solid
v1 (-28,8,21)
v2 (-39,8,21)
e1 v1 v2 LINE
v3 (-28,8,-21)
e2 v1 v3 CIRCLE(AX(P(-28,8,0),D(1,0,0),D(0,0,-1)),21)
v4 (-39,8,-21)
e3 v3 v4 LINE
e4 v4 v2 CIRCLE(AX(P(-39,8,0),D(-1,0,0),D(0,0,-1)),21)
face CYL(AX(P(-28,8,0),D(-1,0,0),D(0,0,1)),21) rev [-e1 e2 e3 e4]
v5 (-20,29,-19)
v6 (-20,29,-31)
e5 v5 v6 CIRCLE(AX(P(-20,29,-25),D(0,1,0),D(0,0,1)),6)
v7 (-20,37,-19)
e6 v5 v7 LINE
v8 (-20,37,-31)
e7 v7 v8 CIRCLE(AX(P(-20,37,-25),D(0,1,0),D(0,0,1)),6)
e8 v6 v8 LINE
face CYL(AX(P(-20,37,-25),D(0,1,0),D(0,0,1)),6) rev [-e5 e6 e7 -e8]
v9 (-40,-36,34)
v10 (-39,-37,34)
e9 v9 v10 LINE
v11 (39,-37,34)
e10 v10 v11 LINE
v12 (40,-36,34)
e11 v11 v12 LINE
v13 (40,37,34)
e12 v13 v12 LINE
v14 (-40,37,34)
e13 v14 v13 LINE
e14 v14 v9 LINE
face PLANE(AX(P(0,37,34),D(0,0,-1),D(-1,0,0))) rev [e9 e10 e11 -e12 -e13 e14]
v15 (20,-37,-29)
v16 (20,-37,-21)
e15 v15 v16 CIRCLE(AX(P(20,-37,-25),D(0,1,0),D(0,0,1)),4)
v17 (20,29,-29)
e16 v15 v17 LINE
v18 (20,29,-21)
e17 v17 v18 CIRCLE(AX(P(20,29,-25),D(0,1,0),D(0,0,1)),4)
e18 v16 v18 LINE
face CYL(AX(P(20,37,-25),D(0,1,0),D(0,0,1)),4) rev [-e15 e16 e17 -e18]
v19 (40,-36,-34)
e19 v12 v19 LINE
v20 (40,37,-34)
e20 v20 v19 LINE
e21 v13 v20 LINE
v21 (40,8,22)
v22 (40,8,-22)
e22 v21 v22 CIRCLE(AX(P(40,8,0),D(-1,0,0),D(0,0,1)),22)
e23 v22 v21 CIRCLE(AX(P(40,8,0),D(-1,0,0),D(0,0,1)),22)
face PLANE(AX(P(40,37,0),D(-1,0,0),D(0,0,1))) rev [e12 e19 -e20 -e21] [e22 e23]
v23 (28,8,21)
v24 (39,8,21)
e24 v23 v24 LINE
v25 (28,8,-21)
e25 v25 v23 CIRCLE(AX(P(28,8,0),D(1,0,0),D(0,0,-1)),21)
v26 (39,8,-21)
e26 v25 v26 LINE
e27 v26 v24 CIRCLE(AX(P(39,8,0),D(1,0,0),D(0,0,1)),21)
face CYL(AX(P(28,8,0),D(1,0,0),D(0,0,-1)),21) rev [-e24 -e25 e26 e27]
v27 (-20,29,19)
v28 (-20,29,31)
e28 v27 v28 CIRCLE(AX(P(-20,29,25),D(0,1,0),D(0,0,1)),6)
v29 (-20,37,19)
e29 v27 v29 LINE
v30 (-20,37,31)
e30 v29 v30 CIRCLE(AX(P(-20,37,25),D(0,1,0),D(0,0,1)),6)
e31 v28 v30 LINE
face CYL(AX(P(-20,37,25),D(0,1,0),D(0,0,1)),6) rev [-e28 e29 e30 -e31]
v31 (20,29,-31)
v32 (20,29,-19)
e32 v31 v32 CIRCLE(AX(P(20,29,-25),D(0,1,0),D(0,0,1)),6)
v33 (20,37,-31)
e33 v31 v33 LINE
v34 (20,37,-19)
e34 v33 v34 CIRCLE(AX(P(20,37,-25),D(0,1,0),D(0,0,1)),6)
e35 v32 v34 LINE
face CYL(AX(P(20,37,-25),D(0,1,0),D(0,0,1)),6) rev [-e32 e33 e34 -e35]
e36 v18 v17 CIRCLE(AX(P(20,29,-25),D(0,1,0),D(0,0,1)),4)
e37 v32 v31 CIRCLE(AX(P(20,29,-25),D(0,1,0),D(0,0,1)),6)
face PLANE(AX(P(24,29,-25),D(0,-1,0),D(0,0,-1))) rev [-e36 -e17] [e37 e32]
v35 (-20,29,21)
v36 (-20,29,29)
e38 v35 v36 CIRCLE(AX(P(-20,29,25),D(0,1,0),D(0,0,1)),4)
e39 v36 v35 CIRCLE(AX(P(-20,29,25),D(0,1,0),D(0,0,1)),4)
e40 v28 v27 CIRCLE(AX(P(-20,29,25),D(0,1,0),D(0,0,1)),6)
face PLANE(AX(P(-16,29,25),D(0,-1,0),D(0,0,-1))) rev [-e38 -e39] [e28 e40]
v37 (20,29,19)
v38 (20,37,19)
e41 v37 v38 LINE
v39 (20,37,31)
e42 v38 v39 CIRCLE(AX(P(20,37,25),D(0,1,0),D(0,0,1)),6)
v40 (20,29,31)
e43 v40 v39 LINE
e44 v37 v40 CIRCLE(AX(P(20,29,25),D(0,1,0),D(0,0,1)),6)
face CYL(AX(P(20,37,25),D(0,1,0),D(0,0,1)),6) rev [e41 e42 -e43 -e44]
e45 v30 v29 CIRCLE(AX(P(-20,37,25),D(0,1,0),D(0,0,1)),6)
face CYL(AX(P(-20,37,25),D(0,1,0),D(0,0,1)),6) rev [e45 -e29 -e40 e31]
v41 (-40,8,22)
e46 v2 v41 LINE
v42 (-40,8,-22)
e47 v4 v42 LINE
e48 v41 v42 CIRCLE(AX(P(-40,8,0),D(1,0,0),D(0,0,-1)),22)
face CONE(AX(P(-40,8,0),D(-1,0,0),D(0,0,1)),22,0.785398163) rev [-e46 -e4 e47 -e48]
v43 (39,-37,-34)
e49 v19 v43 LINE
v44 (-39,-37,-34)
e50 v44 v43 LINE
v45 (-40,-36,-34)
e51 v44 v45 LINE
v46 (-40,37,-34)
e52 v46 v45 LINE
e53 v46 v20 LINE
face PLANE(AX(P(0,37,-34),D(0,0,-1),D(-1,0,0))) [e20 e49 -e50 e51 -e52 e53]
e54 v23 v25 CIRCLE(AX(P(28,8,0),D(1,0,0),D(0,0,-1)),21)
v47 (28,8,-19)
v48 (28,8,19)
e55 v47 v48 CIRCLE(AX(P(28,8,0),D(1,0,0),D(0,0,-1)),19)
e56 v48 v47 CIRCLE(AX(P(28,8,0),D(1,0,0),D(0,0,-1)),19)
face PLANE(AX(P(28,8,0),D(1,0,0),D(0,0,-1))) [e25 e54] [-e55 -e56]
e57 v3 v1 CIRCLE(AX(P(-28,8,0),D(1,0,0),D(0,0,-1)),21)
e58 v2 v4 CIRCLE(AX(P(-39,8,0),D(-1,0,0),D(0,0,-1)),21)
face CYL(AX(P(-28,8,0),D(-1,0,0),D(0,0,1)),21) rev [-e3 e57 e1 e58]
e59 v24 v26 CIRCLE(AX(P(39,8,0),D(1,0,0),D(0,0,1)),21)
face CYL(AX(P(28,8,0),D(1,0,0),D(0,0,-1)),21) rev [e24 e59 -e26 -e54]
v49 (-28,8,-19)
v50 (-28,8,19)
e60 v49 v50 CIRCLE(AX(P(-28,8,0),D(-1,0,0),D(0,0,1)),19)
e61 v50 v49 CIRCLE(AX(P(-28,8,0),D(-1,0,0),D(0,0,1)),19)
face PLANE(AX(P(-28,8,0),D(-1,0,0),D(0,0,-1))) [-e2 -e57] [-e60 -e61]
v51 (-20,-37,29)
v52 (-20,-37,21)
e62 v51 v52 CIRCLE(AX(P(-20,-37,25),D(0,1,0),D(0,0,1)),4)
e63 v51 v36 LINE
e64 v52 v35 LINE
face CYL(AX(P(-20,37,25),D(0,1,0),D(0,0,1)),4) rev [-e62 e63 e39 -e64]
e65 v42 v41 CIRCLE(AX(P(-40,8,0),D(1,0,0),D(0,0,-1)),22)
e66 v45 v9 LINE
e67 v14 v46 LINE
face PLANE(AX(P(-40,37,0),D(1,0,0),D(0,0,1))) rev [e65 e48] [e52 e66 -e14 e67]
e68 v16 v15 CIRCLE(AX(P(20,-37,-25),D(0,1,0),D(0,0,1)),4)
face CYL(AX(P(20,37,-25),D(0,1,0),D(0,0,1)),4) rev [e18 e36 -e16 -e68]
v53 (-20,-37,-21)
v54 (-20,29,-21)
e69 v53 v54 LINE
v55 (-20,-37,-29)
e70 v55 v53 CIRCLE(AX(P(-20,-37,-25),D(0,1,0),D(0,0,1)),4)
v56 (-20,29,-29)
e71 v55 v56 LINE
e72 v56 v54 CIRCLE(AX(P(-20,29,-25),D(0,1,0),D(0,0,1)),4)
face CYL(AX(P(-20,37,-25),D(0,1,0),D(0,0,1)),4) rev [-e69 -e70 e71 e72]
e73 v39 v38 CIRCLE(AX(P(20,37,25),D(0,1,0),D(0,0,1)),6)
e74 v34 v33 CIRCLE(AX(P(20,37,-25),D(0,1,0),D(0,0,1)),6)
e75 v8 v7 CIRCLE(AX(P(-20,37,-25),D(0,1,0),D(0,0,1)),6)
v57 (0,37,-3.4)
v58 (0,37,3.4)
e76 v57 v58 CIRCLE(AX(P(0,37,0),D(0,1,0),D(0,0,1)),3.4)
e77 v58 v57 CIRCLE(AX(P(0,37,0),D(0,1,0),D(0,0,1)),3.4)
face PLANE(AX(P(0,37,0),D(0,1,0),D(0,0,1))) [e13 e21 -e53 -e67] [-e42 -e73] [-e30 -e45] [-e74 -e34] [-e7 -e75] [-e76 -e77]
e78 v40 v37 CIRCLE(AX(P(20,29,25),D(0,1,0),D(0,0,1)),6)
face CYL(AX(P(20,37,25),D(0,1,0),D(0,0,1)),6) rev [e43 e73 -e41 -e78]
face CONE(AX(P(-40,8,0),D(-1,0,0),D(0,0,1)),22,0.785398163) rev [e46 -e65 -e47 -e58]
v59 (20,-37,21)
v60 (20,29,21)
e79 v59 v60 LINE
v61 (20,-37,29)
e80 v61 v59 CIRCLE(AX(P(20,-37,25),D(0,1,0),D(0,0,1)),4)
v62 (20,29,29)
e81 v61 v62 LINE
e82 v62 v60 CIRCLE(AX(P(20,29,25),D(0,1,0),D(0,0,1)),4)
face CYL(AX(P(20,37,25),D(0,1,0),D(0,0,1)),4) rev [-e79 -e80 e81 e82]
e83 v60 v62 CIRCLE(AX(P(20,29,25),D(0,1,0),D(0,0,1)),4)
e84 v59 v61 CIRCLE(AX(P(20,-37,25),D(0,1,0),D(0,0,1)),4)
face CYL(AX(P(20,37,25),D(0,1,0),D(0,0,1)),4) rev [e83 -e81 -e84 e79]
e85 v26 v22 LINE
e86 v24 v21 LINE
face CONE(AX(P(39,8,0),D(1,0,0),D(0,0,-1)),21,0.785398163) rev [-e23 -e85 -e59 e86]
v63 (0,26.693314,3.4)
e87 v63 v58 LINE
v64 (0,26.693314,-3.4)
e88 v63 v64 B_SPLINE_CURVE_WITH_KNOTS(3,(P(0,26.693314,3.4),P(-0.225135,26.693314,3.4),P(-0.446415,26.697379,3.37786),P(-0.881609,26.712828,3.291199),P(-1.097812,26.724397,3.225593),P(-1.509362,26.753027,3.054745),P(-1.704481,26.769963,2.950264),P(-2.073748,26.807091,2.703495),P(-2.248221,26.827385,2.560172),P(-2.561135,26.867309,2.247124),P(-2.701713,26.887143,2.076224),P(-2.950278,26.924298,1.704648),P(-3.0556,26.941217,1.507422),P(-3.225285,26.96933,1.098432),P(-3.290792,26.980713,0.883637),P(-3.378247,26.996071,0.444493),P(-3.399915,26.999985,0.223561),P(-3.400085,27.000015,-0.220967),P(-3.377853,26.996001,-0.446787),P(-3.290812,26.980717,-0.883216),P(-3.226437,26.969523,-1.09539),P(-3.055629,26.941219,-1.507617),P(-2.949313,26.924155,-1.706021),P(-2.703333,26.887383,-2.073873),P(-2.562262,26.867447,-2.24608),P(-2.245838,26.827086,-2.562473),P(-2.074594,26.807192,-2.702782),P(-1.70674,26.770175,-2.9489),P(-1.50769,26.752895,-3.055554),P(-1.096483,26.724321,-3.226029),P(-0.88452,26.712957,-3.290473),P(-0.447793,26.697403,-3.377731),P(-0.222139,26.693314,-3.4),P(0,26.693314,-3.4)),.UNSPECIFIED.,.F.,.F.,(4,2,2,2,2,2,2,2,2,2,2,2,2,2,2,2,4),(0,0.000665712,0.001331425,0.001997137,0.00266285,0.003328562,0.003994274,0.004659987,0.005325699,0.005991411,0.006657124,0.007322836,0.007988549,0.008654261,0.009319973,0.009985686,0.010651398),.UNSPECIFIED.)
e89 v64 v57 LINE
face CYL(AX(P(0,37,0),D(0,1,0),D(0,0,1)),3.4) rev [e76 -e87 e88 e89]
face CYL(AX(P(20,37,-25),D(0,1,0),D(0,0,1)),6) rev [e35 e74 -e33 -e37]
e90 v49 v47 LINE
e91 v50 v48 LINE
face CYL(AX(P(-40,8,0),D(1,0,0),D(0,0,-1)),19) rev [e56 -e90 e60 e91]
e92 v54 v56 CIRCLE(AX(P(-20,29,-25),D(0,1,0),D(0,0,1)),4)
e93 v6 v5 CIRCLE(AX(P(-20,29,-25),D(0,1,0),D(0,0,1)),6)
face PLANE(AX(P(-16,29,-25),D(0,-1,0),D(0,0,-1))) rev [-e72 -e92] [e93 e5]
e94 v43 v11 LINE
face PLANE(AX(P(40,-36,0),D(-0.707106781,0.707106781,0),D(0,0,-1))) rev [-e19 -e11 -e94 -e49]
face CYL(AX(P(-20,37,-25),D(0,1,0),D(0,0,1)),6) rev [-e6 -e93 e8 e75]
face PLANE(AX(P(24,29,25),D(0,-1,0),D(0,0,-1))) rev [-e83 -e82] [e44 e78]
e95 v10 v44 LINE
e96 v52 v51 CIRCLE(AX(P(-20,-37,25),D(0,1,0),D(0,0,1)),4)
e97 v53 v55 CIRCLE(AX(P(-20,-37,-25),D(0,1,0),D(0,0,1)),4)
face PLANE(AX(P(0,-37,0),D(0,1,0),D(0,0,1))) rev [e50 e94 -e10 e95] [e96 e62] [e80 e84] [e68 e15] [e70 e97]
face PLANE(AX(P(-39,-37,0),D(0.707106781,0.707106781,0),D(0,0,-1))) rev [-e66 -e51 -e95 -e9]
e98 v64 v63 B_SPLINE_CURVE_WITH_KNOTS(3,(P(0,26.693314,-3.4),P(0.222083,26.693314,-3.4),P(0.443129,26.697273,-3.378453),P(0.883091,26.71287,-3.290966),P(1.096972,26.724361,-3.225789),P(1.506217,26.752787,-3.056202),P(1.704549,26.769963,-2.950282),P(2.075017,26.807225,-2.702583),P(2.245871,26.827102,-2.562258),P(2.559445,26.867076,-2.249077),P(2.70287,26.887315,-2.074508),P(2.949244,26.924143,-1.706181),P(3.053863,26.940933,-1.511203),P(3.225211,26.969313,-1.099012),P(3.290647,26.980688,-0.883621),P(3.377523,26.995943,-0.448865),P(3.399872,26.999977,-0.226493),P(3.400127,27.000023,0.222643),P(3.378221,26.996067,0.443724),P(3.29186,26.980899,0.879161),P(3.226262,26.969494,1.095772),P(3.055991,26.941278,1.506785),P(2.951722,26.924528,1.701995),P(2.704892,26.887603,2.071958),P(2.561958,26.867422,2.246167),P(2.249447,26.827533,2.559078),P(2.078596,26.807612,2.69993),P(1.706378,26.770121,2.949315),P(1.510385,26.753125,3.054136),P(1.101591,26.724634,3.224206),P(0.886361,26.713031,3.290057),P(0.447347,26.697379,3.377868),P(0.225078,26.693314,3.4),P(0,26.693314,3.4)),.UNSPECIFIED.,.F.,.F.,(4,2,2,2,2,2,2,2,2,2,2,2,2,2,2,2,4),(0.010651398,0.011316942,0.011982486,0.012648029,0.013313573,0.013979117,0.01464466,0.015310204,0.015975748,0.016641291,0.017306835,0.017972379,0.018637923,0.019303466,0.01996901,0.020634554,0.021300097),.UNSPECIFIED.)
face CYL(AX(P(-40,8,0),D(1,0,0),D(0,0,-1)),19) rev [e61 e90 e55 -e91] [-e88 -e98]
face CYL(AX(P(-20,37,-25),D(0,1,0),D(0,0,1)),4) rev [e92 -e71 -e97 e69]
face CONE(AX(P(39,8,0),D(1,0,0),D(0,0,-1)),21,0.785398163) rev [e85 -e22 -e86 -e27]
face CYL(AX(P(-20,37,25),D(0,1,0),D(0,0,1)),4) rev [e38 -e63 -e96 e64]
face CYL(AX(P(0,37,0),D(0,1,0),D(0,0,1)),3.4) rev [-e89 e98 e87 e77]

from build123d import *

# Parameters (mm, degrees)
SKETCH1_W                                            = 40
SKETCH1_H                                            = 68
BOSS_EXTRUDE1_DEPTH                                  = 37
M8_TAPPED_HOLE1_D                                    = 6.8
M8_TAPPED_HOLE1_DEPTH                                = 30
M8_TAPPED_HOLE1_TIP                                  = 2.042926105
SKETCH11_R                                           = 21
CUT_EXTRUDE4_DEPTH                                   = 12
SKETCH12_R                                           = 19
CUT_EXTRUDE5_DEPTH                                   = 85.551759296
CHAMFER1_SIZE                                        = 1
CHAMFER3_SIZE                                        = 1
HOLE_SIZE_PER_SOCKET_HEAD_CAP_SCREW_TYPE_D           = 8
HOLE_SIZE_PER_SOCKET_HEAD_CAP_SCREW_TYPE_CBORE_D     = 12
HOLE_SIZE_PER_SOCKET_HEAD_CAP_SCREW_TYPE_CBORE_DEPTH = 8
MIRROR5_COPY_1_D                                     = 8
MIRROR5_COPY_1_CBORE_D                               = 12
MIRROR5_COPY_1_CBORE_DEPTH                           = 8


with BuildPart() as part:
    # Sketch1 → Boss-Extrude1 (new, symmetric)
    with BuildSketch(Plane(origin=(0, 0, 0), x_dir=(1, 0, 0), z_dir=(0, 1, 0))):
        with Locations((20, 0)):
            Rectangle(SKETCH1_W, SKETCH1_H)
    extrude(amount=BOSS_EXTRUDE1_DEPTH, both=True)

    # Mirror2: part across plane


with BuildPart() as part_1:
    add(part.part)
    add(part.part.mirror(Plane(origin=(0, 37, 0), x_dir=(0, 0, 1), z_dir=(-1, 0, 0))))

    # M8 Tapped Hole1
    with Locations(Plane(origin=(0, 37, 0), x_dir=(1, 0, 0), z_dir=(0, 1, 0))):
        with Locations((0, 0)):
            Hole(M8_TAPPED_HOLE1_D / 2, depth=M8_TAPPED_HOLE1_DEPTH)
            with Locations((0, 0, -(M8_TAPPED_HOLE1_DEPTH + M8_TAPPED_HOLE1_TIP / 2))):  # 118° drill point
                Cone(0, M8_TAPPED_HOLE1_D / 2, M8_TAPPED_HOLE1_TIP, mode=Mode.SUBTRACT)

    # Sketch11 → Cut-Extrude4 (cut)
    with BuildSketch(Plane(origin=(40, 0, 0), x_dir=(0, 0, -1), z_dir=(1, 0, 0))):
        with Locations((0, 8)):
            Circle(SKETCH11_R)
    cut_extrude4 = extrude(amount=-CUT_EXTRUDE4_DEPTH, mode=Mode.SUBTRACT)

    # Mirror3: Cut-Extrude4 across plane
    add(cut_extrude4.mirror(Plane(origin=(0, 0, 0), x_dir=(0, 0, 1), z_dir=(1, 0, 0))), mode=Mode.SUBTRACT)

    # Sketch12 → Cut-Extrude5 (cut, through all)
    with BuildSketch(Plane(origin=(28, 0, 0), x_dir=(0, 0, -1), z_dir=(1, 0, 0))):
        with Locations((0, 8)):
            Circle(SKETCH12_R)
    extrude(amount=-CUT_EXTRUDE5_DEPTH, mode=Mode.SUBTRACT)

    # Chamfer1
    chamfer1_edges = [part_1.edges().sort_by_distance(p)[0] for p in [
        (40, 8, 21),
        (-40, 8, 21),
    ]]
    chamfer(chamfer1_edges, length=CHAMFER1_SIZE)

    # Chamfer3
    chamfer3_edges = [part_1.edges().sort_by_distance(p)[0] for p in [
        (-40, -37, 0),
        (40, -37, 0),
    ]]
    chamfer(chamfer3_edges, length=CHAMFER3_SIZE)

    # Hole size per socket head cap screw type1 (through all)
    with Locations(Plane(origin=(0, 37, 0), x_dir=(1, 0, 0), z_dir=(0, 1, 0))):
        with Locations((-20, -25)):
            hole_size_per_socket_head_cap_screw_type = CounterBoreHole(HOLE_SIZE_PER_SOCKET_HEAD_CAP_SCREW_TYPE_D / 2, HOLE_SIZE_PER_SOCKET_HEAD_CAP_SCREW_TYPE_CBORE_D / 2, HOLE_SIZE_PER_SOCKET_HEAD_CAP_SCREW_TYPE_CBORE_DEPTH)

    # Mirror4: Hole size per socket head cap screw type1 across plane
    add(hole_size_per_socket_head_cap_screw_type.mirror(Plane.XY), mode=Mode.SUBTRACT)

    # Mirror5: Hole size per socket head cap screw type1 across plane
    add(hole_size_per_socket_head_cap_screw_type.mirror(Plane(origin=(0, 0, 0), x_dir=(0, 0, 1), z_dir=(1, 0, 0))), mode=Mode.SUBTRACT)

    # Mirror5 copy 1 (through all)
    with Locations(Plane(origin=(0, 37, 0), x_dir=(-1, 0, 0), z_dir=(0, 1, 0))):
        with Locations((-20, -25)):
            CounterBoreHole(MIRROR5_COPY_1_D / 2, MIRROR5_COPY_1_CBORE_D / 2, MIRROR5_COPY_1_CBORE_DEPTH)


solid = part_1.part
